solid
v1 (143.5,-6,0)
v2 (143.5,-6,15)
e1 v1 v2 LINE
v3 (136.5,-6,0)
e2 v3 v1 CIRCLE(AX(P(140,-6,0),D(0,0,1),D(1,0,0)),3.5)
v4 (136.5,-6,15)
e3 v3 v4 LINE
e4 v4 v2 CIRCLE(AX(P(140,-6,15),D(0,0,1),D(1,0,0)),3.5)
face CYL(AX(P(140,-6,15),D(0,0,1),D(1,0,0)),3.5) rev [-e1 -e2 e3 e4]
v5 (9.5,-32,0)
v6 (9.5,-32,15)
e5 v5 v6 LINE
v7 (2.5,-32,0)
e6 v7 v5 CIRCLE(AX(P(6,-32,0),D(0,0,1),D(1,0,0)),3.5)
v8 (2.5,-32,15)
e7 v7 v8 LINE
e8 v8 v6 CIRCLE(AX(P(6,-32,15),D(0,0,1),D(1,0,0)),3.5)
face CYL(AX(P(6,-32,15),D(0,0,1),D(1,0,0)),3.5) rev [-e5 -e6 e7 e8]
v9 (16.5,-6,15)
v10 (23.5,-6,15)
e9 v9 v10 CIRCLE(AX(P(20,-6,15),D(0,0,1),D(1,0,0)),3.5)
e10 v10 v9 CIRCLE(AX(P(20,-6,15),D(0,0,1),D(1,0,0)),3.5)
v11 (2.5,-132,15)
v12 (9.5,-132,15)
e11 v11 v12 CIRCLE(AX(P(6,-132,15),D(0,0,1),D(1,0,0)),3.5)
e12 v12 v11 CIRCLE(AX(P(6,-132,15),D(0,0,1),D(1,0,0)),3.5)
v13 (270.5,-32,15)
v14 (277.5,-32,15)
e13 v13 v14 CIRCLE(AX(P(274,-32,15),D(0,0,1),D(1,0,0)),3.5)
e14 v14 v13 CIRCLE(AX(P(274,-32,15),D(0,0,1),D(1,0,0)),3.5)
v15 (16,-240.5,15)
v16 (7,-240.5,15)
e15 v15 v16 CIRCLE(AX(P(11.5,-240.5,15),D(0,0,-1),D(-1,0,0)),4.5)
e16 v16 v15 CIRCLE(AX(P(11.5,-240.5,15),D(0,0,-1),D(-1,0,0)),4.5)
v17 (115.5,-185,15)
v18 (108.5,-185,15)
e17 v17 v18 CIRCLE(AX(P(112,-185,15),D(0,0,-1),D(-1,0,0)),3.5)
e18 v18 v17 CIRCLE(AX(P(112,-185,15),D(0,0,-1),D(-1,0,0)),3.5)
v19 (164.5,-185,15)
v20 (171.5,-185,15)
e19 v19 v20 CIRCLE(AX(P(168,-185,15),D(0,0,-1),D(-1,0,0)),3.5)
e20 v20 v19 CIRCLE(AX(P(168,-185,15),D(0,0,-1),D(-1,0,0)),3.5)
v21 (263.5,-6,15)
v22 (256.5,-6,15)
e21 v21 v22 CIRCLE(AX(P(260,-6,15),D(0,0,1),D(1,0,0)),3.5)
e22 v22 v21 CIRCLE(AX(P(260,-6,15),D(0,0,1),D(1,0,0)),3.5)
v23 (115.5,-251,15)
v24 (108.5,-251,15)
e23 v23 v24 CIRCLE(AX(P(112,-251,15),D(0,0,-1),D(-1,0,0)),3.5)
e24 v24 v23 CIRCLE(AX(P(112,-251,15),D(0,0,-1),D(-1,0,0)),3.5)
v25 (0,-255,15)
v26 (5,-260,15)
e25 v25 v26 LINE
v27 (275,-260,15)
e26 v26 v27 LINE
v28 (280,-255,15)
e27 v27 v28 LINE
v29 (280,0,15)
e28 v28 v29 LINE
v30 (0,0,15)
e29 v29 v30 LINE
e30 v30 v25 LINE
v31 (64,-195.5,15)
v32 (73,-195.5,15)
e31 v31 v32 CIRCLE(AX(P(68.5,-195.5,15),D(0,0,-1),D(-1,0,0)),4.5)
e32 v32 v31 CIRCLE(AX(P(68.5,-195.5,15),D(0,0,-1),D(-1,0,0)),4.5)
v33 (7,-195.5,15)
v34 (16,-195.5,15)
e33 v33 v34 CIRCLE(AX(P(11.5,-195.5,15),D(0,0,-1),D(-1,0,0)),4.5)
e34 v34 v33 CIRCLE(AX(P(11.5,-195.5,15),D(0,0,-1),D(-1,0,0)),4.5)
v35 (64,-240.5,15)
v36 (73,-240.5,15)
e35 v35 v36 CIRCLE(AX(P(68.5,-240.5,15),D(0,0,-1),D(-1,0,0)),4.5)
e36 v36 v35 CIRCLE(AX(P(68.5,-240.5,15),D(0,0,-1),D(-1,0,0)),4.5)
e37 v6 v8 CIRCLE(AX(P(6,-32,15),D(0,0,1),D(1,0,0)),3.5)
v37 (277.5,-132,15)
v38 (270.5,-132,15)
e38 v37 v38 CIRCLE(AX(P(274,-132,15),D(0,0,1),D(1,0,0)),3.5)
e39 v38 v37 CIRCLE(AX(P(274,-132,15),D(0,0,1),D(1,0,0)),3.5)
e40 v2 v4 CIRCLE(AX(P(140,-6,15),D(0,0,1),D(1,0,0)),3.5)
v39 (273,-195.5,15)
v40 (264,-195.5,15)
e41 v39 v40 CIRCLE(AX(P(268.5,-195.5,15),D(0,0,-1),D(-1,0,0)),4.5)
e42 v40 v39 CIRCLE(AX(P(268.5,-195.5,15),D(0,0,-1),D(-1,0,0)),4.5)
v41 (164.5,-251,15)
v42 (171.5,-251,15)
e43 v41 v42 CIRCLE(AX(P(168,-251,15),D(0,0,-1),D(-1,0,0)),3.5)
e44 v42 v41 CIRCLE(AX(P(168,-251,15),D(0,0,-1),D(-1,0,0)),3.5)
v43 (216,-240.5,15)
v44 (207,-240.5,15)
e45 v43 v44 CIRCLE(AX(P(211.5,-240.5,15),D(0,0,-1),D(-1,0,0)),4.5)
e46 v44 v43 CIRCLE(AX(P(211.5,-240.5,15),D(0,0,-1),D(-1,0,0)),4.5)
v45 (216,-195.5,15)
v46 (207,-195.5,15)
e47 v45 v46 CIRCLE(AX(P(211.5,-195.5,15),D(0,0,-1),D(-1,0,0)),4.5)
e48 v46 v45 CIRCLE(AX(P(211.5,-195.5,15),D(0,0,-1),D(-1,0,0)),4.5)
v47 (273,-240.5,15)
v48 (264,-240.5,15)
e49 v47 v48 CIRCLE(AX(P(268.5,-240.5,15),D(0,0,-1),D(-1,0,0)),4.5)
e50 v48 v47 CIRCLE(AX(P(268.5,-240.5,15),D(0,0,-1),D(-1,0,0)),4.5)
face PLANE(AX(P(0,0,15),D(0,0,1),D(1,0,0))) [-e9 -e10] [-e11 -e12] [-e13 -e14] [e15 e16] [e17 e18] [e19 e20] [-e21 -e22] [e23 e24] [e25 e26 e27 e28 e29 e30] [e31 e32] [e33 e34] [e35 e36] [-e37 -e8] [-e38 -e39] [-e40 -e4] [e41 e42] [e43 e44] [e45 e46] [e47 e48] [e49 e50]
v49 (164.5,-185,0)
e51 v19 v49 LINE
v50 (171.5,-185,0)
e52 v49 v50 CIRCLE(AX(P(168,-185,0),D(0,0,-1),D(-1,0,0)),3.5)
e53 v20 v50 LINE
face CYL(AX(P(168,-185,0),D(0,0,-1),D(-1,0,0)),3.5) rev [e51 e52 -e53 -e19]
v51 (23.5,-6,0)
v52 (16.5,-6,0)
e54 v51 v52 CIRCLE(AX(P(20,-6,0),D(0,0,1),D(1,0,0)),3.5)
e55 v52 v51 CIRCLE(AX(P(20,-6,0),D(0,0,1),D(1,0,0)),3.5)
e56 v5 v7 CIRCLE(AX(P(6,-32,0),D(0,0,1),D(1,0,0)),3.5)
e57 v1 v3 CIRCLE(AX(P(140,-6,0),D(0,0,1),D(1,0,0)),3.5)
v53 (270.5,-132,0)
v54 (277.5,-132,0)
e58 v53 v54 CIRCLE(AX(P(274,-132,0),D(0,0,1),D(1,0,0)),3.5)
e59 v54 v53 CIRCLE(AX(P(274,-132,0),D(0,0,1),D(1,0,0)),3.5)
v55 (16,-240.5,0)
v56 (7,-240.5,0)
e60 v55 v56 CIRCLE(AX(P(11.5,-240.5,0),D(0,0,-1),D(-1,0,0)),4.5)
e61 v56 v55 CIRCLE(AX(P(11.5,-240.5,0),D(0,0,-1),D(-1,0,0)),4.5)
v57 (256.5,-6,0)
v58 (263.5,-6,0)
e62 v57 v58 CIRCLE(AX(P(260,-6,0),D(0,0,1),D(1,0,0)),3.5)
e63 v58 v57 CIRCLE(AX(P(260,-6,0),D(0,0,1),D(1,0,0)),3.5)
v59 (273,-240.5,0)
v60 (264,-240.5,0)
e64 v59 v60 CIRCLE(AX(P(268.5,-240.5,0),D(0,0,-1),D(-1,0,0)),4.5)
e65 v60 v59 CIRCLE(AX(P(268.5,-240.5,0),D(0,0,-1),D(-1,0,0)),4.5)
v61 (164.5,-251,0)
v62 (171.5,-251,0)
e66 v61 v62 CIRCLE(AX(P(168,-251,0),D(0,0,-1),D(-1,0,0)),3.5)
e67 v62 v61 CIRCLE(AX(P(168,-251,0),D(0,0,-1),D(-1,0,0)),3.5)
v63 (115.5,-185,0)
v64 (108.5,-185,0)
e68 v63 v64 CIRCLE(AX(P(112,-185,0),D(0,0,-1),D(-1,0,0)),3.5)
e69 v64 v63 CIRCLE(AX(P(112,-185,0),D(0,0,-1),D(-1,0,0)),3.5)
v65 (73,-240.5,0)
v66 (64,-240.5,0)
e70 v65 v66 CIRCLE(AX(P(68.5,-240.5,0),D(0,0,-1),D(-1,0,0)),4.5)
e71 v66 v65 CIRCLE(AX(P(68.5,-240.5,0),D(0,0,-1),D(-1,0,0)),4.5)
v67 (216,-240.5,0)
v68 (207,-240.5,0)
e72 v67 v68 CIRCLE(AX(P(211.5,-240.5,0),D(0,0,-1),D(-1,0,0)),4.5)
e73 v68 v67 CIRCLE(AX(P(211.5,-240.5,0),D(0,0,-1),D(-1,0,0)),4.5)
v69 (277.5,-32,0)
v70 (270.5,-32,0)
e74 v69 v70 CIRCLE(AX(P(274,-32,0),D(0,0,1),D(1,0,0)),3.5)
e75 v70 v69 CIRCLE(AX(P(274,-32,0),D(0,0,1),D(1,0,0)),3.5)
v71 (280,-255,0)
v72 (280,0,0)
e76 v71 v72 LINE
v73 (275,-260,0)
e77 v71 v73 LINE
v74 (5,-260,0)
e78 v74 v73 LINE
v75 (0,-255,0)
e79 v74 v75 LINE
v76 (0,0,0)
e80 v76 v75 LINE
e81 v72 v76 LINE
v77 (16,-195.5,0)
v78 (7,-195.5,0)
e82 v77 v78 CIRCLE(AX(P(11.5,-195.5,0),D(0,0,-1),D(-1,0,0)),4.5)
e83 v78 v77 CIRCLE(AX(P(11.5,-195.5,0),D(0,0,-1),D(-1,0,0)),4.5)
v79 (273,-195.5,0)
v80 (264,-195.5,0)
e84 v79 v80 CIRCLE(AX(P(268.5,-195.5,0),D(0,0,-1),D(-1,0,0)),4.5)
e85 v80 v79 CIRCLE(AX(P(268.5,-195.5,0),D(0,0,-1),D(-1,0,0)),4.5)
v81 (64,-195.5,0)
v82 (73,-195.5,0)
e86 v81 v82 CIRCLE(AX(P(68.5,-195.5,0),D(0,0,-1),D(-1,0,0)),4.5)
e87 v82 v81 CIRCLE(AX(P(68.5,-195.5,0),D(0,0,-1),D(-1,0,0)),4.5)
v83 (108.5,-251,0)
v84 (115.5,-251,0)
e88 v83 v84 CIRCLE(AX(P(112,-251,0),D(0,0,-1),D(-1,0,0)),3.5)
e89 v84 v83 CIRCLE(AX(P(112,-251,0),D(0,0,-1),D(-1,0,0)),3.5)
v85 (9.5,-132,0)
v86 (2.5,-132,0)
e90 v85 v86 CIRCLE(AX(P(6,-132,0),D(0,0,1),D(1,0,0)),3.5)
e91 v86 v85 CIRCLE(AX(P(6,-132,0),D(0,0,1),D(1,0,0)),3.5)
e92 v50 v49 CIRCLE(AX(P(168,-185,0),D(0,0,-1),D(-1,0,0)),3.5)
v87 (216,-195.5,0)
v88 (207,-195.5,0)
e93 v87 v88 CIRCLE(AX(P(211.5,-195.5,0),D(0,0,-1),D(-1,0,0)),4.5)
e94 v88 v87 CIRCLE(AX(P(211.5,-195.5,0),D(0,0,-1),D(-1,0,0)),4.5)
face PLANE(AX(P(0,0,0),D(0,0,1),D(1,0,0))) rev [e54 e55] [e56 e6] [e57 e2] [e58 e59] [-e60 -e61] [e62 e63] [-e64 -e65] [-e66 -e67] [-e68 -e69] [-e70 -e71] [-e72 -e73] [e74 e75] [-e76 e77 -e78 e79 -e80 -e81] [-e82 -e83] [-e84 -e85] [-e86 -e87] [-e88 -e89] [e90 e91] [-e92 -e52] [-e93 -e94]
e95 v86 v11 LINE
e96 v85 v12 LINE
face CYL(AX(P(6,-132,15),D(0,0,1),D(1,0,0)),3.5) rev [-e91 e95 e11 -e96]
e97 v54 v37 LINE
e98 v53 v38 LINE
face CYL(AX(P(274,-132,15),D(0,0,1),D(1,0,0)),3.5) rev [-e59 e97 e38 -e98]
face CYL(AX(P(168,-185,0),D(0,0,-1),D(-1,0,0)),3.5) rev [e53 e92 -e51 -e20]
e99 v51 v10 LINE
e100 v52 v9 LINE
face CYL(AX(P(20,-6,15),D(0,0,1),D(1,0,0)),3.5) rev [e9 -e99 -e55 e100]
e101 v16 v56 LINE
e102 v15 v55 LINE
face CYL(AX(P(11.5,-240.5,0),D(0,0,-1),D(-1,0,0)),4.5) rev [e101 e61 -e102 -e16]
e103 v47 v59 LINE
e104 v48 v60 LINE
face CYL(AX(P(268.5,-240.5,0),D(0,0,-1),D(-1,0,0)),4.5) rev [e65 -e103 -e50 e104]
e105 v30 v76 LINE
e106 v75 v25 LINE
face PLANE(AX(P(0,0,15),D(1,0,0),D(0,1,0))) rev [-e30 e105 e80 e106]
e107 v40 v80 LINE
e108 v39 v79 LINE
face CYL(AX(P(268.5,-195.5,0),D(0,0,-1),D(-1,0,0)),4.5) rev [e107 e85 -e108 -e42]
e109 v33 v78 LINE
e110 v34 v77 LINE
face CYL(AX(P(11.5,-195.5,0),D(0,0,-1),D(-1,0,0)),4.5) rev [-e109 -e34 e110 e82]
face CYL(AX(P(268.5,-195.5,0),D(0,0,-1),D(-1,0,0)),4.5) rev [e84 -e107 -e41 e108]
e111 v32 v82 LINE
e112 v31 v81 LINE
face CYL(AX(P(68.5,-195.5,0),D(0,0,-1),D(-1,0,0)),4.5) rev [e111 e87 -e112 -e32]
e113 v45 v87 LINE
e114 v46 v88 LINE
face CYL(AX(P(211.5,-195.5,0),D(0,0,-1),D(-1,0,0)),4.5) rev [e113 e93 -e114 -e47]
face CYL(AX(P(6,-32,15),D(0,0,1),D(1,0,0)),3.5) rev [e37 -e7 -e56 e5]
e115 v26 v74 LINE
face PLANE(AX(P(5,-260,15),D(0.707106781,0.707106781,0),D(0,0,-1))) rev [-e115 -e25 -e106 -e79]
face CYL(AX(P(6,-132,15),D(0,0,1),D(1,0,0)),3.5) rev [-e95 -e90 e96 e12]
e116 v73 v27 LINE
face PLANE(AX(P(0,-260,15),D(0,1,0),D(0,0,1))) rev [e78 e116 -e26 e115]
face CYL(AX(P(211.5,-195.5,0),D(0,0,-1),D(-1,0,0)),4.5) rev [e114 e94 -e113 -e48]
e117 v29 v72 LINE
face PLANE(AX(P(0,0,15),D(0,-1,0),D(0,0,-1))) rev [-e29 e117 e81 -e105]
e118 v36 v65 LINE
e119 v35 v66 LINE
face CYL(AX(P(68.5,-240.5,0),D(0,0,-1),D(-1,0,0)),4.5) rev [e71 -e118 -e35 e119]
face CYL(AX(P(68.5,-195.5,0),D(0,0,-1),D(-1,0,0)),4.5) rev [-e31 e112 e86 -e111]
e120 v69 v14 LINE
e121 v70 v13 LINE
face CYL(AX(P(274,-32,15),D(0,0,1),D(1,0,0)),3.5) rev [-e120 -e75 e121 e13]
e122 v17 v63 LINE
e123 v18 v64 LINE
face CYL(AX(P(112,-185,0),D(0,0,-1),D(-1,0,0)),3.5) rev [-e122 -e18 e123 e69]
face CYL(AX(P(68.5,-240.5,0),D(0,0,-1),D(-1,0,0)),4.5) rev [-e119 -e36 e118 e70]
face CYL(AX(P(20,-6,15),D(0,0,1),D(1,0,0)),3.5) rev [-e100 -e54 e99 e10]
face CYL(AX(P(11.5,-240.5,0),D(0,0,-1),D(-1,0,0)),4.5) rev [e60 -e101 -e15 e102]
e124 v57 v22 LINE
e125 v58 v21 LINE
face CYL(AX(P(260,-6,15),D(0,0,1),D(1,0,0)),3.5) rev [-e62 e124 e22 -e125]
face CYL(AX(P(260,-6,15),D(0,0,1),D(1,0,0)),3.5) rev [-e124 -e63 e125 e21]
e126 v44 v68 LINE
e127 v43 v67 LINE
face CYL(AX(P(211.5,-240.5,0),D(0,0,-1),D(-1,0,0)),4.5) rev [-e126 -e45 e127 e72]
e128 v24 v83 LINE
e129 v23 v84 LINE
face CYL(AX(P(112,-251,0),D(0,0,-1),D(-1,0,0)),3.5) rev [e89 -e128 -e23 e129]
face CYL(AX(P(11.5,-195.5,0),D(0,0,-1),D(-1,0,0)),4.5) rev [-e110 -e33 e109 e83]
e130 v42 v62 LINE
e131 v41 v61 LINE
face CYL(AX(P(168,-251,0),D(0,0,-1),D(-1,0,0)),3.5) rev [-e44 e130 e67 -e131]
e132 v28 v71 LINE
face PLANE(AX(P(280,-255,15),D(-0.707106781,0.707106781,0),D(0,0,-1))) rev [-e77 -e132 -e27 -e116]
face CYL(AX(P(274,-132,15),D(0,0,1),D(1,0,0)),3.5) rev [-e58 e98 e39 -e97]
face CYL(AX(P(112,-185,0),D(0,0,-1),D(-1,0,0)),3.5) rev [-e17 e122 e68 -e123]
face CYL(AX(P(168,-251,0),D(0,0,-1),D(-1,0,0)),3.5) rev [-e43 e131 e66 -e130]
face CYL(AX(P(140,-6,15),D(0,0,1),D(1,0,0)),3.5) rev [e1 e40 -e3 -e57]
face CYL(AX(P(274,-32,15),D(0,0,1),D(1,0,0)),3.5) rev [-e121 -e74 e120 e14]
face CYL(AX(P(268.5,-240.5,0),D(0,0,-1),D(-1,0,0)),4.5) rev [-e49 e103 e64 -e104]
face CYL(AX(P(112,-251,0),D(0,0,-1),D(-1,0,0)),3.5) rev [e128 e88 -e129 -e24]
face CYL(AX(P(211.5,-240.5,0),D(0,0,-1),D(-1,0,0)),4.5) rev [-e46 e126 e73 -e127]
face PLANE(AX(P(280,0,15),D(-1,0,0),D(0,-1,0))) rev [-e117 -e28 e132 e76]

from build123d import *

# Parameters (mm, degrees)
SKETCH_1_W            = 280
SKETCH_1_H            = 260
EXTRUDE_1_DEPTH       = 15
CHAMFER_1_SIZE        = 5
HOLE_WIZARD_7_0_7_3_D = 7
HOLE_WIZARD_7_0_7_2_D = 7
HOLE_WIZARD_9_0_9_1_D = 9
HOLE_WIZARD_7_0_7_1_D = 7


with BuildPart() as part:
    # 草图1 → 凸台-拉伸1 (new body)
    with BuildSketch(Plane.XY):
        with Locations((140, -130)):
            Rectangle(SKETCH_1_W, SKETCH_1_H)
    extrude(amount=EXTRUDE_1_DEPTH)

    # 倒角1
    chamfer_1_edges = [part.edges().sort_by_distance(p)[0] for p in [
        (280, -260, 7.5),
        (0, -260, 7.5),
    ]]
    chamfer(chamfer_1_edges, length=CHAMFER_1_SIZE)

    # Ø7.0 (7) 直径孔3 (through all)
    with Locations(Plane(origin=(0, 0, 0), x_dir=(-1, 0, 0), z_dir=(0, 0, -1))):
        with Locations((-168, -185), (-112, -185), (-112, -251), (-168, -251)):
            Hole(HOLE_WIZARD_7_0_7_3_D / 2)

    # Ø7.0 (7) 直径孔2 (through all)
    with Locations(Plane.XY.offset(15)):
        with Locations((20, -6), (260, -6), (140, -6)):
            Hole(HOLE_WIZARD_7_0_7_2_D / 2)

    # Ø9.0 (9) 直径孔1 (through all)
    with Locations(Plane(origin=(0, 0, 0), x_dir=(-1, 0, 0), z_dir=(0, 0, -1))):
        with Locations((-268.5, -240.5), (-268.5, -195.5), (-211.5, -195.5), (-211.5, -240.5), (-68.5, -240.5), (-68.5, -195.5), (-11.5, -195.5), (-11.5, -240.5)):
            Hole(HOLE_WIZARD_9_0_9_1_D / 2)

    # Ø7.0 (7) 直径孔1 (through all)
    with Locations(Plane.XY.offset(15)):
        with Locations((6, -32), (274, -32), (274, -132), (6, -132)):
            Hole(HOLE_WIZARD_7_0_7_1_D / 2)


solid = part.part
